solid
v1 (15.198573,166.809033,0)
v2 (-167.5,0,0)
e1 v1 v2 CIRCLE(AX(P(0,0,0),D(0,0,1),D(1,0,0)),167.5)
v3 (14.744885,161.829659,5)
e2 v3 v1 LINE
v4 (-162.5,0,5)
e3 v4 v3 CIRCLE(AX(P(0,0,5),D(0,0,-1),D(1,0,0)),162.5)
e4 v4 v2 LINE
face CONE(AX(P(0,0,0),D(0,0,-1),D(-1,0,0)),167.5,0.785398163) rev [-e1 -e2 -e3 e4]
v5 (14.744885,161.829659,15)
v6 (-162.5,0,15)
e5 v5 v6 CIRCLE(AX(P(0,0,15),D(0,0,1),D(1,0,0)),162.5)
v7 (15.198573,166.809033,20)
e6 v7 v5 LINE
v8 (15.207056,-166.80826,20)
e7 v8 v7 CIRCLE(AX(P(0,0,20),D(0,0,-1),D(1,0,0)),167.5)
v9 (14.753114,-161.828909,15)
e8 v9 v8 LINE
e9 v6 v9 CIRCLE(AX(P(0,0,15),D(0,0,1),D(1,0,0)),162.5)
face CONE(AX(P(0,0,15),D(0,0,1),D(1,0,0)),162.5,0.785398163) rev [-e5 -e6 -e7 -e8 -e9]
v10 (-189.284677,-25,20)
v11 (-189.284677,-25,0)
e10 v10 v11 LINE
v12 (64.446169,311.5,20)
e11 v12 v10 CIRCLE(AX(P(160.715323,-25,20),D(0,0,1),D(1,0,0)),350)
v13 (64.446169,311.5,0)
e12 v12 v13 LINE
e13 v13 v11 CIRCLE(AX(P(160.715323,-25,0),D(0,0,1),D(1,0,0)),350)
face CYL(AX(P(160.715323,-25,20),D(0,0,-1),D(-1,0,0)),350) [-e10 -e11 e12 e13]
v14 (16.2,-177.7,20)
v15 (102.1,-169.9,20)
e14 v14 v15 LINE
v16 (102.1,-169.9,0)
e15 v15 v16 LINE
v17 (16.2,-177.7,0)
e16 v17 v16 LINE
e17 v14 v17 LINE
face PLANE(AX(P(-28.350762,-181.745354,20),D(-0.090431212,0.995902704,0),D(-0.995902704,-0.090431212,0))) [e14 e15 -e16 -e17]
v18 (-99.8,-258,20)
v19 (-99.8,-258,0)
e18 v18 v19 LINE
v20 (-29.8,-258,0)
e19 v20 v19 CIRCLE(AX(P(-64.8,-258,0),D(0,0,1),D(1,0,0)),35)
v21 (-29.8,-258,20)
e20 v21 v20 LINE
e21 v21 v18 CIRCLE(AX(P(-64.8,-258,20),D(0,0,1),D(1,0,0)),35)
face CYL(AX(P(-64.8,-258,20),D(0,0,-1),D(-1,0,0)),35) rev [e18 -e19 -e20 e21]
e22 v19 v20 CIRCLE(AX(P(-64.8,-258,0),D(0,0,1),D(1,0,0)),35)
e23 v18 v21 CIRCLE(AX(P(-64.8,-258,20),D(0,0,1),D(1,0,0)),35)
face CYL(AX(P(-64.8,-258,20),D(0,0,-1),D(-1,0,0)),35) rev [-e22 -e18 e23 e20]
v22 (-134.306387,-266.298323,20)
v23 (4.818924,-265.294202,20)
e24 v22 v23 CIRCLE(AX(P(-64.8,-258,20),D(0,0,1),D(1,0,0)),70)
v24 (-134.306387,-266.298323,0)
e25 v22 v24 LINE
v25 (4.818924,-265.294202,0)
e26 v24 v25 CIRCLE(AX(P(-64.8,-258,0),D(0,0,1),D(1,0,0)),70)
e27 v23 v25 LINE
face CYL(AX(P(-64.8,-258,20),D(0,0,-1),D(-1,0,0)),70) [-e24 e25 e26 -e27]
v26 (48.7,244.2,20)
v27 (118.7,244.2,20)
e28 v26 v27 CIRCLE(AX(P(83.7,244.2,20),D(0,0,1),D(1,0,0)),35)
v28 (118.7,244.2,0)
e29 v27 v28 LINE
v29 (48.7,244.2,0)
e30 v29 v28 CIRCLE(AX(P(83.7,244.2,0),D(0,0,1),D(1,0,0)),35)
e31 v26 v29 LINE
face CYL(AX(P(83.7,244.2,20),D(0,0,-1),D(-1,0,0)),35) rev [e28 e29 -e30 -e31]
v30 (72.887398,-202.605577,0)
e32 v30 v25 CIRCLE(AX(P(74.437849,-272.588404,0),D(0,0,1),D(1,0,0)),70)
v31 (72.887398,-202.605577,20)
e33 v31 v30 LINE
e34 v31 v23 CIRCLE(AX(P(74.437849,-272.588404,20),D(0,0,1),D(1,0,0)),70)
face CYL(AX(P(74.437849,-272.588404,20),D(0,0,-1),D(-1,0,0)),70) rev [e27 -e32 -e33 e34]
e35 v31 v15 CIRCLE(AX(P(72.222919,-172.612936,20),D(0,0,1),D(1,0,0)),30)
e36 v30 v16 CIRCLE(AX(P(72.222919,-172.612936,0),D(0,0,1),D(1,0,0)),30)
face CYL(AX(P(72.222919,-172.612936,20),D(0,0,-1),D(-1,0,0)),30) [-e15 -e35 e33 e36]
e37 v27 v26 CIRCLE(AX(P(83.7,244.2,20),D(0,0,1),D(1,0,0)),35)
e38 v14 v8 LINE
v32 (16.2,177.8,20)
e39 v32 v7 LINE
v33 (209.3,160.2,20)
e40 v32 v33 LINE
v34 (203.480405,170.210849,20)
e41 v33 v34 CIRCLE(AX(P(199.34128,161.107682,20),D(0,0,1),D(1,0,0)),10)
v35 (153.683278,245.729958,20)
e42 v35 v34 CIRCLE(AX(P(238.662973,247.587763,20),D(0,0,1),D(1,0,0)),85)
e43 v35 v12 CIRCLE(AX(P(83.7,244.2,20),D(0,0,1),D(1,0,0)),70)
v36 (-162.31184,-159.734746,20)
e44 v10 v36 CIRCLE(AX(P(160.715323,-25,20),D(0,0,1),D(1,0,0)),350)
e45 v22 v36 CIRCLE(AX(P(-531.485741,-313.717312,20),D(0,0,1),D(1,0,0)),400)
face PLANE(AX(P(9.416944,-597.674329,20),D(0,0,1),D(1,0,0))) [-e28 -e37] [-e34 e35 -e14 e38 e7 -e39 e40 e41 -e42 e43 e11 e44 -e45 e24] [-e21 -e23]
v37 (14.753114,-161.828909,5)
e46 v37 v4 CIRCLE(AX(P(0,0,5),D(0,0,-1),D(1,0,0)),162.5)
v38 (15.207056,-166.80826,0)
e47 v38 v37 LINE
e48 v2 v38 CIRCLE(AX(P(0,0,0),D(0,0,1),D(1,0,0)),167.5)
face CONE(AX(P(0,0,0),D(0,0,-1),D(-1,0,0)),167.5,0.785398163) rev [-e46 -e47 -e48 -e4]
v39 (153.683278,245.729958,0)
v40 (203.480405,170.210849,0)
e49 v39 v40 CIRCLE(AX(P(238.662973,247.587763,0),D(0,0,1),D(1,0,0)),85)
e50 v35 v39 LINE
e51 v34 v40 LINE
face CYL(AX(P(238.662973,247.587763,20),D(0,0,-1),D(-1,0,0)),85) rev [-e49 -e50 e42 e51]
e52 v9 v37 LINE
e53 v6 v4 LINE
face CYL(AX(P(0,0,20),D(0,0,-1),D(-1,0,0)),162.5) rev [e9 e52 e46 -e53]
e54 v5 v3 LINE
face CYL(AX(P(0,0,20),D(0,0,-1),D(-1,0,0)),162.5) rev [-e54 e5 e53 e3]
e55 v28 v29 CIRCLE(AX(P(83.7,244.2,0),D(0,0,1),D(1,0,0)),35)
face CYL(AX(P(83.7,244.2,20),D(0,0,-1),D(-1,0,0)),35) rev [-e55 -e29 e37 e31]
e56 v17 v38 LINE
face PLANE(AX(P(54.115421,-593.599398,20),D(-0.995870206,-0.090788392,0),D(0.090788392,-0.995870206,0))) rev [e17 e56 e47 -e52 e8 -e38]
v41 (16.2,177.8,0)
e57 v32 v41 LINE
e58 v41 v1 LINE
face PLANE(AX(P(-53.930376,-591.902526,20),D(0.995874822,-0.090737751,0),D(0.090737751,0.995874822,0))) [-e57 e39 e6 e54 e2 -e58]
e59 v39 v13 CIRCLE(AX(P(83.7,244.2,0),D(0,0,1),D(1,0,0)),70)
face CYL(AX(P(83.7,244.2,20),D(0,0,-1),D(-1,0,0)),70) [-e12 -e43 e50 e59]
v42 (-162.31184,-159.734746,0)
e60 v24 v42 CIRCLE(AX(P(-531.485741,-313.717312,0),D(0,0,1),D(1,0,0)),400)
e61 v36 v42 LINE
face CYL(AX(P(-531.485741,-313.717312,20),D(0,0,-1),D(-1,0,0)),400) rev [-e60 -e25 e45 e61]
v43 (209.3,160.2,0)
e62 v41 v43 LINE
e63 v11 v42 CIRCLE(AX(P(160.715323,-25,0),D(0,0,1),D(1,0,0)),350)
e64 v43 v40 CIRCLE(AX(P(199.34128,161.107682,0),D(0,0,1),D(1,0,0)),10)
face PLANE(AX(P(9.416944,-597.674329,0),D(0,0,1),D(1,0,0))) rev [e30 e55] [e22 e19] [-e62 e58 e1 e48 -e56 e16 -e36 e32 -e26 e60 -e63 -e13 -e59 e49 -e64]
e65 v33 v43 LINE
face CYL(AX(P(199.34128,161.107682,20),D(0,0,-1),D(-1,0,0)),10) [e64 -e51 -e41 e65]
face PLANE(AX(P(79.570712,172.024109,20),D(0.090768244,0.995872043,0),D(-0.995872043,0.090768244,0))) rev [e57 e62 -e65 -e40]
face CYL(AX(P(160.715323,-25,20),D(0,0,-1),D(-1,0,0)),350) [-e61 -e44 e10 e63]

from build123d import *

# Parameters (mm, degrees)
SKETCH1_R           = 35
BOSS_EXTRUDE1_DEPTH = 20
CHAMFER1_SIZE       = 5


with BuildPart() as part:
    # Sketch1 → Boss-Extrude1 (new body)
    with BuildSketch(Plane.XY):
        with BuildLine():
            ThreePointArc((72.887397787, -202.60557658), (27.017010086, -221.097976732), (4.818924287, -265.294201888))
            ThreePointArc((4.818924287, -265.294201888), (-64.294796067, -327.998176898), (-134.306386999, -266.298323103))
            ThreePointArc((-134.306386999, -266.298323103), (-144.622358434, -212.04763629), (-162.31184025, -159.734745723))
            ThreePointArc((-162.31184025, -159.734745723), (-154.669991707, 126.763312998), (64.446169212, 311.5))
            ThreePointArc((64.446169212, 311.5), (125.230637191, 300.548967821), (153.683278213, 245.729957687))
            ThreePointArc((153.683278213, 245.729957687), (167.70153078, 200.795951222), (203.480405215, 170.210848864))
            ThreePointArc((203.480405215, 170.210848864), (207.986601411, 166.133457037), (209.3, 160.2))
            Line((209.3, 160.2), (16.2, 177.8))
            Line((16.2, 177.8), (14.744884523, 161.829658531))
            ThreePointArc((14.744884523, 161.829658531), (-162.499999947, -0.00413168), (14.753113776, -161.828908523))
            Line((14.753113776, -161.828908523), (16.2, -177.7))
            Line((16.2, -177.7), (102.1, -169.9))
            ThreePointArc((102.1, -169.9), (94.597243609, -192.597670349), (72.887397787, -202.60557658))
        make_face()
        with Locations((-64.8, -258)):
            Circle(SKETCH1_R, mode=Mode.SUBTRACT)
        with Locations((83.7, 244.2)):
            Circle(SKETCH1_R, mode=Mode.SUBTRACT)
    extrude(amount=BOSS_EXTRUDE1_DEPTH)

    # Chamfer1
    chamfer1_edges = [part.edges().sort_by_distance(p)[0] for p in [
        (-162.499999947, -0.00413168, 0),
        (-162.499999947, -0.00413168, 20),
    ]]
    chamfer(chamfer1_edges, length=CHAMFER1_SIZE)


solid = part.part
